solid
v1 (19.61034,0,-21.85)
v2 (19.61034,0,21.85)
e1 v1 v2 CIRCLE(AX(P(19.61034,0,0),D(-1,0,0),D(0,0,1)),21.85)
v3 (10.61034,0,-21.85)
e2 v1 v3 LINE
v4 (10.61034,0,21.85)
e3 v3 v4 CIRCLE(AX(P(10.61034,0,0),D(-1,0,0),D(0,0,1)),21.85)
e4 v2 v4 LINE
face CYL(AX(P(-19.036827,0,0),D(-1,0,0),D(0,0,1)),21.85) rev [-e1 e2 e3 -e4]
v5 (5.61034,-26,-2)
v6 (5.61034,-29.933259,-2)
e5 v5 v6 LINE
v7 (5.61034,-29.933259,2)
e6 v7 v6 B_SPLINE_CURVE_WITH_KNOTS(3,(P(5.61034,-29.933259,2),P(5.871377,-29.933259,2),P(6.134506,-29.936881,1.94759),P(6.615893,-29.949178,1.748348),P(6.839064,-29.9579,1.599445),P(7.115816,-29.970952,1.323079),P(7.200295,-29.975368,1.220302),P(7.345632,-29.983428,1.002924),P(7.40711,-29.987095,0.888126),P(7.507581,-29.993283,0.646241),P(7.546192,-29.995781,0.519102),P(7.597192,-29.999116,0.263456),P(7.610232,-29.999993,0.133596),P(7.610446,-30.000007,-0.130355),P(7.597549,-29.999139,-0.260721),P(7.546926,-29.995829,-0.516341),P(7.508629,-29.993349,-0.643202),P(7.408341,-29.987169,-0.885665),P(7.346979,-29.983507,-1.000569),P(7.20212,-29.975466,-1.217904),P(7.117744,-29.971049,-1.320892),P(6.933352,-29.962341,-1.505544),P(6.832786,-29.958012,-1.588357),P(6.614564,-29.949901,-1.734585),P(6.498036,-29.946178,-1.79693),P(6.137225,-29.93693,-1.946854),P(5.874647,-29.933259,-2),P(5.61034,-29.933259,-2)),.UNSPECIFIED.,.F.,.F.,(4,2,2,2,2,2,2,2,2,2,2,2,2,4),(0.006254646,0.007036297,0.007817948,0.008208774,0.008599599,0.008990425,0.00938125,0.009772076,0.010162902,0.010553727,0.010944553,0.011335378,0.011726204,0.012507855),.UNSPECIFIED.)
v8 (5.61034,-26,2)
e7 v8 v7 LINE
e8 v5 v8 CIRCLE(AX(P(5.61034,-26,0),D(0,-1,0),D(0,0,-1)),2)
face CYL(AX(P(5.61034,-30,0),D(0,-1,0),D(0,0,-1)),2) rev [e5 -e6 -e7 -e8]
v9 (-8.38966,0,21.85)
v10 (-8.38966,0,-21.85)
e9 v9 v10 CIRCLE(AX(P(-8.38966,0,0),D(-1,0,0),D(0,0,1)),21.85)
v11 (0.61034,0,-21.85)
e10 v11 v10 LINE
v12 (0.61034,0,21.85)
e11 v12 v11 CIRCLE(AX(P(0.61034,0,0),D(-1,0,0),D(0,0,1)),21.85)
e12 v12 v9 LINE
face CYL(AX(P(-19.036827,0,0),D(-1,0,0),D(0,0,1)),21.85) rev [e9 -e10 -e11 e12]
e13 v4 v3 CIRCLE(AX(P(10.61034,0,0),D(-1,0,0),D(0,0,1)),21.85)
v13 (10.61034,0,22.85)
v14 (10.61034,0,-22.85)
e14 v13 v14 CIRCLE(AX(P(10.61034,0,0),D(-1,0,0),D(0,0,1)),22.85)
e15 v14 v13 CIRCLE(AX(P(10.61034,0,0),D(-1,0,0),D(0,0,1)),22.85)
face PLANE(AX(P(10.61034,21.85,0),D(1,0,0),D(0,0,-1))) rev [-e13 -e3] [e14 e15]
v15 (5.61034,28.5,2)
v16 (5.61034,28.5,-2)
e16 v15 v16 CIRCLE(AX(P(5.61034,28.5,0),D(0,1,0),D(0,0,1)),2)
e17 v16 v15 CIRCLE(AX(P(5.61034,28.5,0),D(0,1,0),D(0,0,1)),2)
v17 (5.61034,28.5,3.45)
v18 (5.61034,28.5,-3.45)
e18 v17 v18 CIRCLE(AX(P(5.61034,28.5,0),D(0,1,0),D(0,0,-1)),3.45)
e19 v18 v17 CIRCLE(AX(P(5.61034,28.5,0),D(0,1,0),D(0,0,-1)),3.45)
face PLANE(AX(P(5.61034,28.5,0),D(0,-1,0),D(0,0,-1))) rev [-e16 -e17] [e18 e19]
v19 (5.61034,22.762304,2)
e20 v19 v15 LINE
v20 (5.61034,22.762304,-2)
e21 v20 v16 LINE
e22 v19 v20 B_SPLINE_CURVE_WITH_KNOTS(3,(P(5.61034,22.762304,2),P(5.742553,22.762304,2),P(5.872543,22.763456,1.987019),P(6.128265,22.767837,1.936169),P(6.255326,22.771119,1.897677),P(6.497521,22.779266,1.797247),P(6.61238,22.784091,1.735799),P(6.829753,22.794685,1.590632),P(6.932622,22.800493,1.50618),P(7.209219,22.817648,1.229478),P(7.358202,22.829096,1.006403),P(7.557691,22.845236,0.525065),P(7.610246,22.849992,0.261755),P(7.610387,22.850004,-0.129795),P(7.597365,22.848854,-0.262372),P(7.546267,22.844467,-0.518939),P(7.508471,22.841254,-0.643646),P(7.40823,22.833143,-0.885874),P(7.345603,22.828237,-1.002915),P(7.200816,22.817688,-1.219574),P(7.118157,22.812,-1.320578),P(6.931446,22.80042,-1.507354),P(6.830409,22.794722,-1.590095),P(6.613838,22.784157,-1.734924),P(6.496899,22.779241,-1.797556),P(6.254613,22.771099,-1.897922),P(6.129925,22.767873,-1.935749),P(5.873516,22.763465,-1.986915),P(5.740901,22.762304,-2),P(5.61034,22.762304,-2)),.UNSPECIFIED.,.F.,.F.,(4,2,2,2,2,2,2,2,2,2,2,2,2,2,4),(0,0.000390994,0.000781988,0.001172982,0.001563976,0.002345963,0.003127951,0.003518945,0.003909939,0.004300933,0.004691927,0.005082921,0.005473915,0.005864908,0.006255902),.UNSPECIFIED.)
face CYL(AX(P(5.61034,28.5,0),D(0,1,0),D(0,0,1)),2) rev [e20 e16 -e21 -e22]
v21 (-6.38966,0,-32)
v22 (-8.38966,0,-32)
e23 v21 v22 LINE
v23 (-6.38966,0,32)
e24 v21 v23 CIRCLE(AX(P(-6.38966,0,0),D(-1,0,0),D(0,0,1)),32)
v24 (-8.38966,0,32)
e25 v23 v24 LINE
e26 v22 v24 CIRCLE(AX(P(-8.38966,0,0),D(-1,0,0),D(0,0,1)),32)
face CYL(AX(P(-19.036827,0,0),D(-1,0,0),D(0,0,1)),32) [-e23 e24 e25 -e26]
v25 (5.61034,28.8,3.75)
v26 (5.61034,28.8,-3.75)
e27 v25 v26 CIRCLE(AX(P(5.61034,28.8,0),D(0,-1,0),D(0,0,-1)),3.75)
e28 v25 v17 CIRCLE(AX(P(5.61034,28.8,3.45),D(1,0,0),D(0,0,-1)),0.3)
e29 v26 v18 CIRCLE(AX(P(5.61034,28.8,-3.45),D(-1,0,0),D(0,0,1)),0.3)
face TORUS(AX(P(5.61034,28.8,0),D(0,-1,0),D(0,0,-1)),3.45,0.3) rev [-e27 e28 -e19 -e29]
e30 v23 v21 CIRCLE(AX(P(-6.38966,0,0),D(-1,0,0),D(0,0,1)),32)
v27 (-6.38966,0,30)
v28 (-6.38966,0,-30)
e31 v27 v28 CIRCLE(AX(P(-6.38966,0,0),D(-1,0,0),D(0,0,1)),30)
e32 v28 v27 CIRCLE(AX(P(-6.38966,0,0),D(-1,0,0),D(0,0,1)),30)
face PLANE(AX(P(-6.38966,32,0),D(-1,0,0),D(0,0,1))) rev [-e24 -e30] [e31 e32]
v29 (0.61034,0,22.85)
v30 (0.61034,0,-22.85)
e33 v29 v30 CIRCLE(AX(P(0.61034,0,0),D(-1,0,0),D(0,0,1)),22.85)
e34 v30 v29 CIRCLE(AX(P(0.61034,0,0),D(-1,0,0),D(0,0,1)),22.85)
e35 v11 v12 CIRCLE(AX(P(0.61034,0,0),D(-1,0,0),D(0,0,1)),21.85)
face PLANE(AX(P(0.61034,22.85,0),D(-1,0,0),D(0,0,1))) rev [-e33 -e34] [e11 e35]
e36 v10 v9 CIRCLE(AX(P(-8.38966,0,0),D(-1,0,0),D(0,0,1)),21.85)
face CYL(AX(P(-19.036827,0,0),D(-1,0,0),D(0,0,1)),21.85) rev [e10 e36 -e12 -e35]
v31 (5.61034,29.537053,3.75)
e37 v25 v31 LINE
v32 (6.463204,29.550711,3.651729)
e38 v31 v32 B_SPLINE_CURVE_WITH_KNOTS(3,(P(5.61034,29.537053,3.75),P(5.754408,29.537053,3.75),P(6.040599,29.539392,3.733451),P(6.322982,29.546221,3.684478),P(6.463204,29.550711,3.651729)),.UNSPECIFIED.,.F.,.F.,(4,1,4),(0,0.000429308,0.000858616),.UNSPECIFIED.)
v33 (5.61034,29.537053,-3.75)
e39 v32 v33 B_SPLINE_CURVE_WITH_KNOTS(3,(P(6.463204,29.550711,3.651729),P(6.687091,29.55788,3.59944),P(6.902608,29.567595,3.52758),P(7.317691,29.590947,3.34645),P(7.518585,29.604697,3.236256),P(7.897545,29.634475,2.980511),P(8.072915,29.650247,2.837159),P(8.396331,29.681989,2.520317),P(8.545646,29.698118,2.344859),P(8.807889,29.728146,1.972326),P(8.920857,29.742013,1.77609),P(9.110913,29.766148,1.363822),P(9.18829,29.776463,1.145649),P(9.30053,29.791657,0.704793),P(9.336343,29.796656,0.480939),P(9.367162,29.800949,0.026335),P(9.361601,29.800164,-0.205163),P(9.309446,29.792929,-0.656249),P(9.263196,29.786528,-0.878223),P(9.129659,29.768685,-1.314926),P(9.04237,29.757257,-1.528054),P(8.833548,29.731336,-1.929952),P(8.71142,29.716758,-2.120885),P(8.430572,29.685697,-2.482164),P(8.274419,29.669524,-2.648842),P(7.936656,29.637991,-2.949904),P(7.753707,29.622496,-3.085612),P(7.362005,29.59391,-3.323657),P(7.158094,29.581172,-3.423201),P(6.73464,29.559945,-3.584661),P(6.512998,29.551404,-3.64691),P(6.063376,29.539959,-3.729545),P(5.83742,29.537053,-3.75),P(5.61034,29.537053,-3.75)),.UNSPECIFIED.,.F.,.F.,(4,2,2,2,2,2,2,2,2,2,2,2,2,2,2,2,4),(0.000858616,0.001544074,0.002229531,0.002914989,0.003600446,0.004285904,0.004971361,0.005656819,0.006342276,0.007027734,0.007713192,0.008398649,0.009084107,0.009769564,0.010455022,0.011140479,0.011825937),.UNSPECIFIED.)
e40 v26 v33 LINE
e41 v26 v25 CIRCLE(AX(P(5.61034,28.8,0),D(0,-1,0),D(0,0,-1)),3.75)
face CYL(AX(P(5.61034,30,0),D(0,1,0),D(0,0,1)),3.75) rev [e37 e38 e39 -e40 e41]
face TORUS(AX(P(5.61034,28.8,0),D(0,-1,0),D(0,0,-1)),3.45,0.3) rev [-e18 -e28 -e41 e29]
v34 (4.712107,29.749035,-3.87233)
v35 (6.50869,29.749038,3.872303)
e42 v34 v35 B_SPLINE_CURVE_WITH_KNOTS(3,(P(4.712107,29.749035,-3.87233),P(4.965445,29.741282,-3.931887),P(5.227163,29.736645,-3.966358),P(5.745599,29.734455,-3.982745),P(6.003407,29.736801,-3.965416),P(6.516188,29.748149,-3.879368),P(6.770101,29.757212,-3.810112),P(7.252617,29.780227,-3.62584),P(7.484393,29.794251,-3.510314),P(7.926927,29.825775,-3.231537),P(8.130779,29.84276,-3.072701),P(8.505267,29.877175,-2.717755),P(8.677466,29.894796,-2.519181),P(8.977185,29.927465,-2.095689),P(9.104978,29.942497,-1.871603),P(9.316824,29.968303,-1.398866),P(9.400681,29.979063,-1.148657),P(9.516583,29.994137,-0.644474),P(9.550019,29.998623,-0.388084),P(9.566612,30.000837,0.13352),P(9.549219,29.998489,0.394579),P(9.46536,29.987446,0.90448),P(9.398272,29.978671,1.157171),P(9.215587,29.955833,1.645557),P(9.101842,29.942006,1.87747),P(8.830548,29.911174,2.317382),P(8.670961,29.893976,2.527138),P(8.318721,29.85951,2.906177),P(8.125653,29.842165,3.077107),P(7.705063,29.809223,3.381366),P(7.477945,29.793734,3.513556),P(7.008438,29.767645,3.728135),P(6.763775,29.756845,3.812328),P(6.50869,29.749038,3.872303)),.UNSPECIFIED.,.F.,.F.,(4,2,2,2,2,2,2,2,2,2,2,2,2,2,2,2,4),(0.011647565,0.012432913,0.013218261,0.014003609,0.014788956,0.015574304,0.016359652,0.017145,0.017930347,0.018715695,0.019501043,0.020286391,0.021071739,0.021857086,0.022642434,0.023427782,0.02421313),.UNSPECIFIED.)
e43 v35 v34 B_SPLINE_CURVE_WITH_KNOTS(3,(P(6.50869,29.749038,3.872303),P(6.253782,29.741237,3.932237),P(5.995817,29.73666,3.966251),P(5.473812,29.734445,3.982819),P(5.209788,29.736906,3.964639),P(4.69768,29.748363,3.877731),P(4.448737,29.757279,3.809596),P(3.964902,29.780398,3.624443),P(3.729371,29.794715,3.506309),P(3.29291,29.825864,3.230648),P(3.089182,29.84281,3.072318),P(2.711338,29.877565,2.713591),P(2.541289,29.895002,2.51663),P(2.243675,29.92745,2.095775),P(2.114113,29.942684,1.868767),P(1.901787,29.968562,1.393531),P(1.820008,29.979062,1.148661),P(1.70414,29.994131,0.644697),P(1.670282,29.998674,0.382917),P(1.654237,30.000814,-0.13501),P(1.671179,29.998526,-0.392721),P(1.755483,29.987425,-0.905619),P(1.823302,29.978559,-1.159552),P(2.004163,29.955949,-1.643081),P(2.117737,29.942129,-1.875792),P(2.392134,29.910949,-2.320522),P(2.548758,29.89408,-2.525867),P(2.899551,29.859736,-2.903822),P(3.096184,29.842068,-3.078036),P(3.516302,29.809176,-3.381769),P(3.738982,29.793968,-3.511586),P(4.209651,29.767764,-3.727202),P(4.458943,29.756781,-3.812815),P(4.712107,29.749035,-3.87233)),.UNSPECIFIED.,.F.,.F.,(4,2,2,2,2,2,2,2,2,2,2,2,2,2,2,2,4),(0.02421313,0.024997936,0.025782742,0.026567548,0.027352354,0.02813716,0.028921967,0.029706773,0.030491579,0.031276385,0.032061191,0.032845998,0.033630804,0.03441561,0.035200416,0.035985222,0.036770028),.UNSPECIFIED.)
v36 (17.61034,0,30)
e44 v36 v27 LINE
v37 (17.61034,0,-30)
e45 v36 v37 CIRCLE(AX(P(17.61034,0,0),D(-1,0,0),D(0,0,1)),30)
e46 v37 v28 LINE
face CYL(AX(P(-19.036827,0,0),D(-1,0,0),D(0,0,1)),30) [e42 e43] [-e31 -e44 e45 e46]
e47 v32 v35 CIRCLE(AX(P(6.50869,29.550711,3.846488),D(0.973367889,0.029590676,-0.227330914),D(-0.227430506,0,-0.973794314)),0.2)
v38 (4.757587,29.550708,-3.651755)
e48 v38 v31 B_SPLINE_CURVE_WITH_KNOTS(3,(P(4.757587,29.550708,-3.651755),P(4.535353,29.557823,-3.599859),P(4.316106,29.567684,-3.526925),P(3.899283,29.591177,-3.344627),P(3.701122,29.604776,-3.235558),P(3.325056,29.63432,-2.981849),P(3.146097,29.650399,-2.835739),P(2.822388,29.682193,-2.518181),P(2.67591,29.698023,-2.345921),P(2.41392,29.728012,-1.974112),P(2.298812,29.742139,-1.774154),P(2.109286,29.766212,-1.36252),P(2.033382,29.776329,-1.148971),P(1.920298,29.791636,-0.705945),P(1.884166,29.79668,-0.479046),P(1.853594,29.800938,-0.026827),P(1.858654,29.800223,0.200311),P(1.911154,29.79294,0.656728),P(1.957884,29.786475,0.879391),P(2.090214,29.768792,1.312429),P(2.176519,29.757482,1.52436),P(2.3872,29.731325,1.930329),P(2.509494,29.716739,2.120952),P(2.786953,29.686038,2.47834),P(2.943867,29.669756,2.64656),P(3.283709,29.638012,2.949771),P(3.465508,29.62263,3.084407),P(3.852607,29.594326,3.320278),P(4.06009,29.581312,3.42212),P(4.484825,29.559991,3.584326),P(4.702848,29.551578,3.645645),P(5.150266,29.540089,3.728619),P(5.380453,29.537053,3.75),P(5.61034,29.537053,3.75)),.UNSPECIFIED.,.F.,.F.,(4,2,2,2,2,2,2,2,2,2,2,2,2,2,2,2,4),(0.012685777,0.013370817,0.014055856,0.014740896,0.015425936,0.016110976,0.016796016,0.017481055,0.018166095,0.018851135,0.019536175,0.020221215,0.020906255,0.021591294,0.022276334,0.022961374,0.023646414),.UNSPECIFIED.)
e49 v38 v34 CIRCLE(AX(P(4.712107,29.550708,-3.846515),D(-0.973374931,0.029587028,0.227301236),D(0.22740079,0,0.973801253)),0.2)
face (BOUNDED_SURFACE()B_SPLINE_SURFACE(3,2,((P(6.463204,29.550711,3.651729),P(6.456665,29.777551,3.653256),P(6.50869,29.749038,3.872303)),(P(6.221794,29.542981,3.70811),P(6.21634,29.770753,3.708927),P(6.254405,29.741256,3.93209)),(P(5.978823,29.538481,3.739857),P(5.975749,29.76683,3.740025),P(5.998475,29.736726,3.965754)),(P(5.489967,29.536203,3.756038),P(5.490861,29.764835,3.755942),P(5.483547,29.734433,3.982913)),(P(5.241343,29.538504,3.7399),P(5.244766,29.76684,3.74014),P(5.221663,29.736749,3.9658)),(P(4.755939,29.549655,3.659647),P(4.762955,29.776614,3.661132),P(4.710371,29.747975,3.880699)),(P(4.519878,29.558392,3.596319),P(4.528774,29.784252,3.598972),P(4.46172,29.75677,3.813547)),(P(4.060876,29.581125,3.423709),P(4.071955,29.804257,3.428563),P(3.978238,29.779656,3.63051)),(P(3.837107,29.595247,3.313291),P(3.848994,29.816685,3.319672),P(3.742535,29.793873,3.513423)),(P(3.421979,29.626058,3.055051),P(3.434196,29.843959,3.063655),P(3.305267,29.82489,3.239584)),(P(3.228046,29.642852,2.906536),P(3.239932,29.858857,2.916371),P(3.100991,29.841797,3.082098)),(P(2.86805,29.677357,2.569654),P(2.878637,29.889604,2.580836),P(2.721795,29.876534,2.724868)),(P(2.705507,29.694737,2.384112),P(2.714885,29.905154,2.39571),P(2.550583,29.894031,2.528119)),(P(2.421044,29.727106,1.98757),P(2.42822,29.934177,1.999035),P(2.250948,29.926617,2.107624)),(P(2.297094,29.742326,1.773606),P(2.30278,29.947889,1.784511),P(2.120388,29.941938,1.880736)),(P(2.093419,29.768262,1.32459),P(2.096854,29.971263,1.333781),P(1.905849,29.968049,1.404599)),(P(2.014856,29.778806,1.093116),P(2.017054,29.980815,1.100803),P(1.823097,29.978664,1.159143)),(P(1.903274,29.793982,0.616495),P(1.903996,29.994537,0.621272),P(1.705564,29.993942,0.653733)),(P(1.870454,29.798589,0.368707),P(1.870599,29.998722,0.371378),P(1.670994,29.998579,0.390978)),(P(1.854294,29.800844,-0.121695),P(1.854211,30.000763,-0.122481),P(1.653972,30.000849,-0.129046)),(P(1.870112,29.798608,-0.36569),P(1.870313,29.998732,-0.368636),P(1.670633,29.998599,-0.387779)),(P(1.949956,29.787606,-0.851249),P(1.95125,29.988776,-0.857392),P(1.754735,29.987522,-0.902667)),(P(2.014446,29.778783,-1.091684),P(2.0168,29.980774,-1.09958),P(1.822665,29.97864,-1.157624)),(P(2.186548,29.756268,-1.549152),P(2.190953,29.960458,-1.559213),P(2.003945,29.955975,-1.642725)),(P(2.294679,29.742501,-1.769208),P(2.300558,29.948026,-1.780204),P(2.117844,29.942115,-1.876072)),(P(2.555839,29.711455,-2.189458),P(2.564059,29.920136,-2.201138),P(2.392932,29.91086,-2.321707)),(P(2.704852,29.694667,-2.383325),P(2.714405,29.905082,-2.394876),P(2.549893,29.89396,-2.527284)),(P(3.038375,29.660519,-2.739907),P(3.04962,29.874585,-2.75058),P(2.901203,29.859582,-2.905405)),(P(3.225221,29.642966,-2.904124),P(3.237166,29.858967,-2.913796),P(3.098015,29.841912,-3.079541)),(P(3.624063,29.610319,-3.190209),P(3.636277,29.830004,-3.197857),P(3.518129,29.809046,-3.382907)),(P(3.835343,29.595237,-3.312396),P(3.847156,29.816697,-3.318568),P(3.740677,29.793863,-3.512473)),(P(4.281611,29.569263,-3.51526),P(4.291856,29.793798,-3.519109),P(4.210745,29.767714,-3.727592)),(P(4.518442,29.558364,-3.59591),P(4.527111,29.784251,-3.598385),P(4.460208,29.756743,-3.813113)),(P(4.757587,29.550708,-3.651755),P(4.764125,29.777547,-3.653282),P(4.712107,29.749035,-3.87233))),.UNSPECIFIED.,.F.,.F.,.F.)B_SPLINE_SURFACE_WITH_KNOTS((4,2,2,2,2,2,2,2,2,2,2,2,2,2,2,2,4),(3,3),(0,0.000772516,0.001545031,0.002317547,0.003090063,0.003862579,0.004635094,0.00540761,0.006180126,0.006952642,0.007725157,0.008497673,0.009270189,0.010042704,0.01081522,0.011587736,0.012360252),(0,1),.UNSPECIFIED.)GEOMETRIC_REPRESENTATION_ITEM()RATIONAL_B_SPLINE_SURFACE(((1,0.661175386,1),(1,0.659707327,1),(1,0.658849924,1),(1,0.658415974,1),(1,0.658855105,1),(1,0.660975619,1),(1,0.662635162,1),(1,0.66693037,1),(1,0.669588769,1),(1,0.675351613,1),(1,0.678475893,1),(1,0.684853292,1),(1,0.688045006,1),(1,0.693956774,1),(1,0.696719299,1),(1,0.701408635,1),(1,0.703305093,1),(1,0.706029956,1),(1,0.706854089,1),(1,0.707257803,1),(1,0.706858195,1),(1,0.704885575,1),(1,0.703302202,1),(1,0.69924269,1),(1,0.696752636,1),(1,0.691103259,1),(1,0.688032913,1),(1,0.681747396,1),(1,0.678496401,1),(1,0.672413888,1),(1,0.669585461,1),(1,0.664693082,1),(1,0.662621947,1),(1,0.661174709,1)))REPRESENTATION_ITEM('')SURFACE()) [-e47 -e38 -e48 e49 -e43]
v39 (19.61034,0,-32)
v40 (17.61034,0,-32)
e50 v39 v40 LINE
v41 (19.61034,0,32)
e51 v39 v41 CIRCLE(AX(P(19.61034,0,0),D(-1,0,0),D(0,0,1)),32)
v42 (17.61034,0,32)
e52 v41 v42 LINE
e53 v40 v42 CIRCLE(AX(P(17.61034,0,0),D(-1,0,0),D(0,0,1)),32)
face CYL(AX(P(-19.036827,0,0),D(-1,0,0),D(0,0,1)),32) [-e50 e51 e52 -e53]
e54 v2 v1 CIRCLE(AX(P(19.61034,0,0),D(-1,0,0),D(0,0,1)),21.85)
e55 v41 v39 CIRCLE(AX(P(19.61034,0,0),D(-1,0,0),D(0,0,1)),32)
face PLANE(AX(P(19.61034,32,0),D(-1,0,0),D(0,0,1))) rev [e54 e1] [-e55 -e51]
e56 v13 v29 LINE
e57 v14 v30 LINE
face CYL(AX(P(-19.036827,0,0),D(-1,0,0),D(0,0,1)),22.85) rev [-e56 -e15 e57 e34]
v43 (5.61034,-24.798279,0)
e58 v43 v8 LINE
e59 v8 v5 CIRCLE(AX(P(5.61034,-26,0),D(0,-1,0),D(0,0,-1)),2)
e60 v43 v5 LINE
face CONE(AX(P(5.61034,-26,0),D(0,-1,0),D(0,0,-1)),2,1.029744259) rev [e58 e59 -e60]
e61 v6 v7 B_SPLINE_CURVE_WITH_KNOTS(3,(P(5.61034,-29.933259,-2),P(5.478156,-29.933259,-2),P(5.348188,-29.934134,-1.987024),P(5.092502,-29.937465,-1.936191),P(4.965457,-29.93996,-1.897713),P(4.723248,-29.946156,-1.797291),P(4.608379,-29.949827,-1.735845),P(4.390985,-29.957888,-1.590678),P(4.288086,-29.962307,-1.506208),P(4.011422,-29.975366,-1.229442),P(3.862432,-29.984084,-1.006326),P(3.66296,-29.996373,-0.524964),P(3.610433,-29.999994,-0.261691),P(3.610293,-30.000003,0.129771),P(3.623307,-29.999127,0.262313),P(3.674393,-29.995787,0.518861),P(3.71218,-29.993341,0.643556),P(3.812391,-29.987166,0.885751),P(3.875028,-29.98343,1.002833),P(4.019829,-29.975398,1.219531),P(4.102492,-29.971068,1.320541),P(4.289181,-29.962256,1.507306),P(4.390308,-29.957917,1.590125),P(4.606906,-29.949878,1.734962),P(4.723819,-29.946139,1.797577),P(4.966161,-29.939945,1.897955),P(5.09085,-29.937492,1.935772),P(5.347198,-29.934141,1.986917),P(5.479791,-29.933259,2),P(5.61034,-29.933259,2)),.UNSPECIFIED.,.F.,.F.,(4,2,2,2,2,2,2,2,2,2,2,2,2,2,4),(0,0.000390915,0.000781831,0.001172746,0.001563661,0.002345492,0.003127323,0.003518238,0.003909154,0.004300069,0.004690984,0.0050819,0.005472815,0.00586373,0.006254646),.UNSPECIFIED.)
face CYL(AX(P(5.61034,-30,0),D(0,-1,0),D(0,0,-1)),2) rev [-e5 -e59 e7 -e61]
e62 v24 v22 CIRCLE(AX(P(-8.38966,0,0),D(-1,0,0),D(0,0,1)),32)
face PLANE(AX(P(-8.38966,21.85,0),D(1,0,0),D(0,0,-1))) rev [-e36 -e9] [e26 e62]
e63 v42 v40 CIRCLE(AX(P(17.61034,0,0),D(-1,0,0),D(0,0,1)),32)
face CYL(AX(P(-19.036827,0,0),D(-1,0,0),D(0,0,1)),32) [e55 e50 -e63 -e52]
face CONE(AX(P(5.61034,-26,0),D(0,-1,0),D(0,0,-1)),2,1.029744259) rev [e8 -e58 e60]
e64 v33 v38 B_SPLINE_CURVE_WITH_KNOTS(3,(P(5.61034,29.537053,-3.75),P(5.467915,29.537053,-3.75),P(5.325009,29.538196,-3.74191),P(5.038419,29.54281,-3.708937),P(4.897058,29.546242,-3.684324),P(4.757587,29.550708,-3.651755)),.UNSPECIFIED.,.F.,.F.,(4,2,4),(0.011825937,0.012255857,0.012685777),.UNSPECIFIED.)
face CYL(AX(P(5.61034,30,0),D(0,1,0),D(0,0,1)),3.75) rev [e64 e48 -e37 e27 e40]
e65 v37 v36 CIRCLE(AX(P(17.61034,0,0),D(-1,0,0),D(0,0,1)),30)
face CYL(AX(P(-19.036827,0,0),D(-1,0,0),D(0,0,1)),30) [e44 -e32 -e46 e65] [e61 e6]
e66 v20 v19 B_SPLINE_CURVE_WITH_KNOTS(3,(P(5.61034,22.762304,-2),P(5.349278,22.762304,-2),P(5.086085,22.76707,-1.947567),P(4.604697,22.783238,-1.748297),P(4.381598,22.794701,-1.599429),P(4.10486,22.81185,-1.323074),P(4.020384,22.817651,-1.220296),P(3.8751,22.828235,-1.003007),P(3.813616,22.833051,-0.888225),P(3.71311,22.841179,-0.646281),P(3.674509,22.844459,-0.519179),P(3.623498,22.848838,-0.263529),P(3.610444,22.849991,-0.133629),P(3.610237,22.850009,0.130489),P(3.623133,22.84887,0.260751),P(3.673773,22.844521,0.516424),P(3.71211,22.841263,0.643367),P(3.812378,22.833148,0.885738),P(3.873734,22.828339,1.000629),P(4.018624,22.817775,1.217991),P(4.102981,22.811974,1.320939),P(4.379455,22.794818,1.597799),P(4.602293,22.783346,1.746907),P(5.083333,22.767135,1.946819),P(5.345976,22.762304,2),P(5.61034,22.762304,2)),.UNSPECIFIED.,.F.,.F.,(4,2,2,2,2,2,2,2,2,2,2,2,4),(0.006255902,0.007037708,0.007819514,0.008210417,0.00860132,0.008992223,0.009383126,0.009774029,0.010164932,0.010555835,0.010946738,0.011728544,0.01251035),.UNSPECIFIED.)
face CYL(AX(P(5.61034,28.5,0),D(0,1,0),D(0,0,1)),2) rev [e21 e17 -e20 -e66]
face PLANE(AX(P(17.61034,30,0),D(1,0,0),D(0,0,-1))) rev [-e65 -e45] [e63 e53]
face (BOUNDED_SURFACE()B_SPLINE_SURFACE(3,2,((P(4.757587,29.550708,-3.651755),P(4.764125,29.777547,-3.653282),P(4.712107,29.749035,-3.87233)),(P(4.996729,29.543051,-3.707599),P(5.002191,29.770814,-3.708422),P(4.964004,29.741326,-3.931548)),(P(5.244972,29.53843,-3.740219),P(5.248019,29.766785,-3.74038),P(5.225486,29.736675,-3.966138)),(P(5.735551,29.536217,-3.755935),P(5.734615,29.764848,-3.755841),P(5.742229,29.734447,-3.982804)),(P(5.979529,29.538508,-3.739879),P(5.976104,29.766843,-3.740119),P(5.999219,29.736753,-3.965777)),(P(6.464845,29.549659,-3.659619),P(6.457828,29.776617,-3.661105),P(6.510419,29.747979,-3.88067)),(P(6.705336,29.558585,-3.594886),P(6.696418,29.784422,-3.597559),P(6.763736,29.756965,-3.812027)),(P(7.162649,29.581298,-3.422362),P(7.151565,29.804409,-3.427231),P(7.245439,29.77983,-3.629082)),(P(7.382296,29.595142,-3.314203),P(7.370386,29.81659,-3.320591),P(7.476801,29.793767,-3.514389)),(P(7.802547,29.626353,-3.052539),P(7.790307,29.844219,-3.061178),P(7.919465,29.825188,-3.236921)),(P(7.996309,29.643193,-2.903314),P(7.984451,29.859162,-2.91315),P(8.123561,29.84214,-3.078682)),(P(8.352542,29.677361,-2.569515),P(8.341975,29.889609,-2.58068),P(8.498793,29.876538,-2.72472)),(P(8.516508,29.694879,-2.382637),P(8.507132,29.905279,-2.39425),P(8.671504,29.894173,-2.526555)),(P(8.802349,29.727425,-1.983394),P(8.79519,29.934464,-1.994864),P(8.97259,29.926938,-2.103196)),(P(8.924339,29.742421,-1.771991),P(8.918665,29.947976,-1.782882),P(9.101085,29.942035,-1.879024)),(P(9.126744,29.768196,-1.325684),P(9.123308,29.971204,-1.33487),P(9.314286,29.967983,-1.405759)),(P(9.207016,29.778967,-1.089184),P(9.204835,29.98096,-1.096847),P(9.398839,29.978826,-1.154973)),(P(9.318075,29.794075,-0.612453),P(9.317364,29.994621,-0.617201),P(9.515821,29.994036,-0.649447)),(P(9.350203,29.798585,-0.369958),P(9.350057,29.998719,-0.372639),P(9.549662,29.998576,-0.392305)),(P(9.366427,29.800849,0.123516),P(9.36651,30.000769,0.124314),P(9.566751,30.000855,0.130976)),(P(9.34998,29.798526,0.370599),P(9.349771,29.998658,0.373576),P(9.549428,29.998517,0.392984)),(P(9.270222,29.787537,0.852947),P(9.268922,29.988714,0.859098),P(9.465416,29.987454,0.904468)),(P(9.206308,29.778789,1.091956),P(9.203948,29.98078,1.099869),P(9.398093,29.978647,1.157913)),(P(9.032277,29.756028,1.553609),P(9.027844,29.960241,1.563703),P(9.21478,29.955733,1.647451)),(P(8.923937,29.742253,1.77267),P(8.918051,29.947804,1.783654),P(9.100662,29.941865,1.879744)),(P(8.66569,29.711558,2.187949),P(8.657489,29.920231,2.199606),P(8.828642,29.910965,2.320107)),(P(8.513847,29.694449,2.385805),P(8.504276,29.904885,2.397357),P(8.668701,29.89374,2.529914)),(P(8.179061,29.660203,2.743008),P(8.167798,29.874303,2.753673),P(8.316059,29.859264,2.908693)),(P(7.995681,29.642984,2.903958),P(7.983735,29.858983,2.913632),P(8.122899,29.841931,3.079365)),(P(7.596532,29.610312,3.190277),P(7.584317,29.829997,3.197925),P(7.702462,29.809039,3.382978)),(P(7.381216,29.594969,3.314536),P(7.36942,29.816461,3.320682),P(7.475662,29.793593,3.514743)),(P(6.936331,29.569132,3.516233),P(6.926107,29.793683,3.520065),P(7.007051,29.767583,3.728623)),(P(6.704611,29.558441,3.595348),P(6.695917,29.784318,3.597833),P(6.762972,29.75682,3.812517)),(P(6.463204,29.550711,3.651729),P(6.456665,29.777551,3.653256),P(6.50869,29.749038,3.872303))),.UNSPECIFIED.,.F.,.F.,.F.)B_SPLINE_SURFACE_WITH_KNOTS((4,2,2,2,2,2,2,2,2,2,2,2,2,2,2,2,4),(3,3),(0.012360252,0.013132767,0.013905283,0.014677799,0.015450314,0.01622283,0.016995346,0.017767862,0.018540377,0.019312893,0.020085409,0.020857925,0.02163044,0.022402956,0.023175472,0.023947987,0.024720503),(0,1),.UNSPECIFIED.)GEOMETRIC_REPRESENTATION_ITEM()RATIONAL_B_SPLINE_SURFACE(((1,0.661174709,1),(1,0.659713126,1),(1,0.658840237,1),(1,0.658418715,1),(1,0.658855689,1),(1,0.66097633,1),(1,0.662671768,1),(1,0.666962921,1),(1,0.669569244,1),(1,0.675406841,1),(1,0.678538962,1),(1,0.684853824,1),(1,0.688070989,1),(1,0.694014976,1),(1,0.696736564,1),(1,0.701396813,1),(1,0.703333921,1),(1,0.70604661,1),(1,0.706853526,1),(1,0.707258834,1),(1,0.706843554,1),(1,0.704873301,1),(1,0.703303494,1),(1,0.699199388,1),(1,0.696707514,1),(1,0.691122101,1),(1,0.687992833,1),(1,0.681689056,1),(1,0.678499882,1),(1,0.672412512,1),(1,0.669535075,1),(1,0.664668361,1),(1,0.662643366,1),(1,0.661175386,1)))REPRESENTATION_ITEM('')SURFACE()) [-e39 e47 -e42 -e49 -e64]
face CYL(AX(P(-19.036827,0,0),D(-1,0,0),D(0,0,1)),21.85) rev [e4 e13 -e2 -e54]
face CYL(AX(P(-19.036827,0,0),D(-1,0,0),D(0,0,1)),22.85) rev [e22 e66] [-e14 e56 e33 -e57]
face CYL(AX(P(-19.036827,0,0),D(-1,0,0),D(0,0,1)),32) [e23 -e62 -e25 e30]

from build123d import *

# Parameters (mm, degrees)
HOLE1_D           = 7.5
HOLE1_DEPTH       = 1.5
HOLE2_REACH       = 73.196
HOLE2_BORE_R      = 2
DOWEL_HOLE1_D     = 4
DOWEL_HOLE1_DEPTH = 4
DOWEL_HOLE1_TIP   = 1.201721238
FILLET1_R         = 0.2
FILLET2_R         = 0.3


with BuildPart() as part:
    # Sketch1 → Revolve1 (revolve)
    with BuildSketch(Plane.XY, mode=Mode.PRIVATE) as revolve1_sk:
        Polygon((-8.389660143, 21.85), (-8.389660143, 32), (-6.389660143, 32), (-6.389660143, 30), (17.610339857, 30), (17.610339857, 32), (19.610339857, 32), (19.610339857, 21.85), (10.610339857, 21.85), (10.610339857, 22.85), (0.610339857, 22.85), (0.610339857, 21.85), align=None)
    revolve(revolve1_sk.sketch.rotate(Axis((-19.036826505, 0, 0), (1, 0, 0)), 90), axis=Axis((-19.036826505, 0, 0), (1, 0, 0)))

    # Hole1
    with Locations(Plane(origin=(0, 30, 0), x_dir=(1, 0, 0), z_dir=(0, 1, 0))):
        with Locations((5.610339857, 0)):
            Hole(HOLE1_D / 2, depth=HOLE1_DEPTH)

    # Hole2 bore → Hole2 (cut, up to next)
    with BuildSketch(Plane(origin=(0, 28.5, 0), x_dir=(1, 0, 0), z_dir=(0, 1, 0)), mode=Mode.PRIVATE) as hole2_sk1:
        with Locations((5.610339857, 0)):
            Circle(HOLE2_BORE_R)
    hole2_tool1 = extrude(hole2_sk1.sketch, amount=-HOLE2_REACH, mode=Mode.PRIVATE) & part.part
    add(hole2_tool1.solids().sort_by_distance((5.61034, 28.5, 0))[0], mode=Mode.SUBTRACT)

    # Dowel Hole1
    with Locations(Plane(origin=(0, -30, 0), x_dir=(-1, 0, 0), z_dir=(0, -1, 0))):
        with Locations((-5.610339857, 0)):
            Hole(DOWEL_HOLE1_D / 2, depth=DOWEL_HOLE1_DEPTH)
            with Locations((0, 0, -(DOWEL_HOLE1_DEPTH + DOWEL_HOLE1_TIP / 2))):  # 118° drill point
                Cone(0, DOWEL_HOLE1_D / 2, DOWEL_HOLE1_TIP, mode=Mode.SUBTRACT)

    # Fillet1
    fillet1_edges = [part.edges().sort_by_distance(p)[0] for p in [
        (9.360339864, 29.999999997, -1e-09),
    ]]
    fillet(fillet1_edges, radius=FILLET1_R)

    # Fillet2
    fillet2_edges = [part.edges().sort_by_distance(p)[0] for p in [
        (9.360339857, 28.5, 0),
    ]]
    fillet(fillet2_edges, radius=FILLET2_R)


solid = part.part
